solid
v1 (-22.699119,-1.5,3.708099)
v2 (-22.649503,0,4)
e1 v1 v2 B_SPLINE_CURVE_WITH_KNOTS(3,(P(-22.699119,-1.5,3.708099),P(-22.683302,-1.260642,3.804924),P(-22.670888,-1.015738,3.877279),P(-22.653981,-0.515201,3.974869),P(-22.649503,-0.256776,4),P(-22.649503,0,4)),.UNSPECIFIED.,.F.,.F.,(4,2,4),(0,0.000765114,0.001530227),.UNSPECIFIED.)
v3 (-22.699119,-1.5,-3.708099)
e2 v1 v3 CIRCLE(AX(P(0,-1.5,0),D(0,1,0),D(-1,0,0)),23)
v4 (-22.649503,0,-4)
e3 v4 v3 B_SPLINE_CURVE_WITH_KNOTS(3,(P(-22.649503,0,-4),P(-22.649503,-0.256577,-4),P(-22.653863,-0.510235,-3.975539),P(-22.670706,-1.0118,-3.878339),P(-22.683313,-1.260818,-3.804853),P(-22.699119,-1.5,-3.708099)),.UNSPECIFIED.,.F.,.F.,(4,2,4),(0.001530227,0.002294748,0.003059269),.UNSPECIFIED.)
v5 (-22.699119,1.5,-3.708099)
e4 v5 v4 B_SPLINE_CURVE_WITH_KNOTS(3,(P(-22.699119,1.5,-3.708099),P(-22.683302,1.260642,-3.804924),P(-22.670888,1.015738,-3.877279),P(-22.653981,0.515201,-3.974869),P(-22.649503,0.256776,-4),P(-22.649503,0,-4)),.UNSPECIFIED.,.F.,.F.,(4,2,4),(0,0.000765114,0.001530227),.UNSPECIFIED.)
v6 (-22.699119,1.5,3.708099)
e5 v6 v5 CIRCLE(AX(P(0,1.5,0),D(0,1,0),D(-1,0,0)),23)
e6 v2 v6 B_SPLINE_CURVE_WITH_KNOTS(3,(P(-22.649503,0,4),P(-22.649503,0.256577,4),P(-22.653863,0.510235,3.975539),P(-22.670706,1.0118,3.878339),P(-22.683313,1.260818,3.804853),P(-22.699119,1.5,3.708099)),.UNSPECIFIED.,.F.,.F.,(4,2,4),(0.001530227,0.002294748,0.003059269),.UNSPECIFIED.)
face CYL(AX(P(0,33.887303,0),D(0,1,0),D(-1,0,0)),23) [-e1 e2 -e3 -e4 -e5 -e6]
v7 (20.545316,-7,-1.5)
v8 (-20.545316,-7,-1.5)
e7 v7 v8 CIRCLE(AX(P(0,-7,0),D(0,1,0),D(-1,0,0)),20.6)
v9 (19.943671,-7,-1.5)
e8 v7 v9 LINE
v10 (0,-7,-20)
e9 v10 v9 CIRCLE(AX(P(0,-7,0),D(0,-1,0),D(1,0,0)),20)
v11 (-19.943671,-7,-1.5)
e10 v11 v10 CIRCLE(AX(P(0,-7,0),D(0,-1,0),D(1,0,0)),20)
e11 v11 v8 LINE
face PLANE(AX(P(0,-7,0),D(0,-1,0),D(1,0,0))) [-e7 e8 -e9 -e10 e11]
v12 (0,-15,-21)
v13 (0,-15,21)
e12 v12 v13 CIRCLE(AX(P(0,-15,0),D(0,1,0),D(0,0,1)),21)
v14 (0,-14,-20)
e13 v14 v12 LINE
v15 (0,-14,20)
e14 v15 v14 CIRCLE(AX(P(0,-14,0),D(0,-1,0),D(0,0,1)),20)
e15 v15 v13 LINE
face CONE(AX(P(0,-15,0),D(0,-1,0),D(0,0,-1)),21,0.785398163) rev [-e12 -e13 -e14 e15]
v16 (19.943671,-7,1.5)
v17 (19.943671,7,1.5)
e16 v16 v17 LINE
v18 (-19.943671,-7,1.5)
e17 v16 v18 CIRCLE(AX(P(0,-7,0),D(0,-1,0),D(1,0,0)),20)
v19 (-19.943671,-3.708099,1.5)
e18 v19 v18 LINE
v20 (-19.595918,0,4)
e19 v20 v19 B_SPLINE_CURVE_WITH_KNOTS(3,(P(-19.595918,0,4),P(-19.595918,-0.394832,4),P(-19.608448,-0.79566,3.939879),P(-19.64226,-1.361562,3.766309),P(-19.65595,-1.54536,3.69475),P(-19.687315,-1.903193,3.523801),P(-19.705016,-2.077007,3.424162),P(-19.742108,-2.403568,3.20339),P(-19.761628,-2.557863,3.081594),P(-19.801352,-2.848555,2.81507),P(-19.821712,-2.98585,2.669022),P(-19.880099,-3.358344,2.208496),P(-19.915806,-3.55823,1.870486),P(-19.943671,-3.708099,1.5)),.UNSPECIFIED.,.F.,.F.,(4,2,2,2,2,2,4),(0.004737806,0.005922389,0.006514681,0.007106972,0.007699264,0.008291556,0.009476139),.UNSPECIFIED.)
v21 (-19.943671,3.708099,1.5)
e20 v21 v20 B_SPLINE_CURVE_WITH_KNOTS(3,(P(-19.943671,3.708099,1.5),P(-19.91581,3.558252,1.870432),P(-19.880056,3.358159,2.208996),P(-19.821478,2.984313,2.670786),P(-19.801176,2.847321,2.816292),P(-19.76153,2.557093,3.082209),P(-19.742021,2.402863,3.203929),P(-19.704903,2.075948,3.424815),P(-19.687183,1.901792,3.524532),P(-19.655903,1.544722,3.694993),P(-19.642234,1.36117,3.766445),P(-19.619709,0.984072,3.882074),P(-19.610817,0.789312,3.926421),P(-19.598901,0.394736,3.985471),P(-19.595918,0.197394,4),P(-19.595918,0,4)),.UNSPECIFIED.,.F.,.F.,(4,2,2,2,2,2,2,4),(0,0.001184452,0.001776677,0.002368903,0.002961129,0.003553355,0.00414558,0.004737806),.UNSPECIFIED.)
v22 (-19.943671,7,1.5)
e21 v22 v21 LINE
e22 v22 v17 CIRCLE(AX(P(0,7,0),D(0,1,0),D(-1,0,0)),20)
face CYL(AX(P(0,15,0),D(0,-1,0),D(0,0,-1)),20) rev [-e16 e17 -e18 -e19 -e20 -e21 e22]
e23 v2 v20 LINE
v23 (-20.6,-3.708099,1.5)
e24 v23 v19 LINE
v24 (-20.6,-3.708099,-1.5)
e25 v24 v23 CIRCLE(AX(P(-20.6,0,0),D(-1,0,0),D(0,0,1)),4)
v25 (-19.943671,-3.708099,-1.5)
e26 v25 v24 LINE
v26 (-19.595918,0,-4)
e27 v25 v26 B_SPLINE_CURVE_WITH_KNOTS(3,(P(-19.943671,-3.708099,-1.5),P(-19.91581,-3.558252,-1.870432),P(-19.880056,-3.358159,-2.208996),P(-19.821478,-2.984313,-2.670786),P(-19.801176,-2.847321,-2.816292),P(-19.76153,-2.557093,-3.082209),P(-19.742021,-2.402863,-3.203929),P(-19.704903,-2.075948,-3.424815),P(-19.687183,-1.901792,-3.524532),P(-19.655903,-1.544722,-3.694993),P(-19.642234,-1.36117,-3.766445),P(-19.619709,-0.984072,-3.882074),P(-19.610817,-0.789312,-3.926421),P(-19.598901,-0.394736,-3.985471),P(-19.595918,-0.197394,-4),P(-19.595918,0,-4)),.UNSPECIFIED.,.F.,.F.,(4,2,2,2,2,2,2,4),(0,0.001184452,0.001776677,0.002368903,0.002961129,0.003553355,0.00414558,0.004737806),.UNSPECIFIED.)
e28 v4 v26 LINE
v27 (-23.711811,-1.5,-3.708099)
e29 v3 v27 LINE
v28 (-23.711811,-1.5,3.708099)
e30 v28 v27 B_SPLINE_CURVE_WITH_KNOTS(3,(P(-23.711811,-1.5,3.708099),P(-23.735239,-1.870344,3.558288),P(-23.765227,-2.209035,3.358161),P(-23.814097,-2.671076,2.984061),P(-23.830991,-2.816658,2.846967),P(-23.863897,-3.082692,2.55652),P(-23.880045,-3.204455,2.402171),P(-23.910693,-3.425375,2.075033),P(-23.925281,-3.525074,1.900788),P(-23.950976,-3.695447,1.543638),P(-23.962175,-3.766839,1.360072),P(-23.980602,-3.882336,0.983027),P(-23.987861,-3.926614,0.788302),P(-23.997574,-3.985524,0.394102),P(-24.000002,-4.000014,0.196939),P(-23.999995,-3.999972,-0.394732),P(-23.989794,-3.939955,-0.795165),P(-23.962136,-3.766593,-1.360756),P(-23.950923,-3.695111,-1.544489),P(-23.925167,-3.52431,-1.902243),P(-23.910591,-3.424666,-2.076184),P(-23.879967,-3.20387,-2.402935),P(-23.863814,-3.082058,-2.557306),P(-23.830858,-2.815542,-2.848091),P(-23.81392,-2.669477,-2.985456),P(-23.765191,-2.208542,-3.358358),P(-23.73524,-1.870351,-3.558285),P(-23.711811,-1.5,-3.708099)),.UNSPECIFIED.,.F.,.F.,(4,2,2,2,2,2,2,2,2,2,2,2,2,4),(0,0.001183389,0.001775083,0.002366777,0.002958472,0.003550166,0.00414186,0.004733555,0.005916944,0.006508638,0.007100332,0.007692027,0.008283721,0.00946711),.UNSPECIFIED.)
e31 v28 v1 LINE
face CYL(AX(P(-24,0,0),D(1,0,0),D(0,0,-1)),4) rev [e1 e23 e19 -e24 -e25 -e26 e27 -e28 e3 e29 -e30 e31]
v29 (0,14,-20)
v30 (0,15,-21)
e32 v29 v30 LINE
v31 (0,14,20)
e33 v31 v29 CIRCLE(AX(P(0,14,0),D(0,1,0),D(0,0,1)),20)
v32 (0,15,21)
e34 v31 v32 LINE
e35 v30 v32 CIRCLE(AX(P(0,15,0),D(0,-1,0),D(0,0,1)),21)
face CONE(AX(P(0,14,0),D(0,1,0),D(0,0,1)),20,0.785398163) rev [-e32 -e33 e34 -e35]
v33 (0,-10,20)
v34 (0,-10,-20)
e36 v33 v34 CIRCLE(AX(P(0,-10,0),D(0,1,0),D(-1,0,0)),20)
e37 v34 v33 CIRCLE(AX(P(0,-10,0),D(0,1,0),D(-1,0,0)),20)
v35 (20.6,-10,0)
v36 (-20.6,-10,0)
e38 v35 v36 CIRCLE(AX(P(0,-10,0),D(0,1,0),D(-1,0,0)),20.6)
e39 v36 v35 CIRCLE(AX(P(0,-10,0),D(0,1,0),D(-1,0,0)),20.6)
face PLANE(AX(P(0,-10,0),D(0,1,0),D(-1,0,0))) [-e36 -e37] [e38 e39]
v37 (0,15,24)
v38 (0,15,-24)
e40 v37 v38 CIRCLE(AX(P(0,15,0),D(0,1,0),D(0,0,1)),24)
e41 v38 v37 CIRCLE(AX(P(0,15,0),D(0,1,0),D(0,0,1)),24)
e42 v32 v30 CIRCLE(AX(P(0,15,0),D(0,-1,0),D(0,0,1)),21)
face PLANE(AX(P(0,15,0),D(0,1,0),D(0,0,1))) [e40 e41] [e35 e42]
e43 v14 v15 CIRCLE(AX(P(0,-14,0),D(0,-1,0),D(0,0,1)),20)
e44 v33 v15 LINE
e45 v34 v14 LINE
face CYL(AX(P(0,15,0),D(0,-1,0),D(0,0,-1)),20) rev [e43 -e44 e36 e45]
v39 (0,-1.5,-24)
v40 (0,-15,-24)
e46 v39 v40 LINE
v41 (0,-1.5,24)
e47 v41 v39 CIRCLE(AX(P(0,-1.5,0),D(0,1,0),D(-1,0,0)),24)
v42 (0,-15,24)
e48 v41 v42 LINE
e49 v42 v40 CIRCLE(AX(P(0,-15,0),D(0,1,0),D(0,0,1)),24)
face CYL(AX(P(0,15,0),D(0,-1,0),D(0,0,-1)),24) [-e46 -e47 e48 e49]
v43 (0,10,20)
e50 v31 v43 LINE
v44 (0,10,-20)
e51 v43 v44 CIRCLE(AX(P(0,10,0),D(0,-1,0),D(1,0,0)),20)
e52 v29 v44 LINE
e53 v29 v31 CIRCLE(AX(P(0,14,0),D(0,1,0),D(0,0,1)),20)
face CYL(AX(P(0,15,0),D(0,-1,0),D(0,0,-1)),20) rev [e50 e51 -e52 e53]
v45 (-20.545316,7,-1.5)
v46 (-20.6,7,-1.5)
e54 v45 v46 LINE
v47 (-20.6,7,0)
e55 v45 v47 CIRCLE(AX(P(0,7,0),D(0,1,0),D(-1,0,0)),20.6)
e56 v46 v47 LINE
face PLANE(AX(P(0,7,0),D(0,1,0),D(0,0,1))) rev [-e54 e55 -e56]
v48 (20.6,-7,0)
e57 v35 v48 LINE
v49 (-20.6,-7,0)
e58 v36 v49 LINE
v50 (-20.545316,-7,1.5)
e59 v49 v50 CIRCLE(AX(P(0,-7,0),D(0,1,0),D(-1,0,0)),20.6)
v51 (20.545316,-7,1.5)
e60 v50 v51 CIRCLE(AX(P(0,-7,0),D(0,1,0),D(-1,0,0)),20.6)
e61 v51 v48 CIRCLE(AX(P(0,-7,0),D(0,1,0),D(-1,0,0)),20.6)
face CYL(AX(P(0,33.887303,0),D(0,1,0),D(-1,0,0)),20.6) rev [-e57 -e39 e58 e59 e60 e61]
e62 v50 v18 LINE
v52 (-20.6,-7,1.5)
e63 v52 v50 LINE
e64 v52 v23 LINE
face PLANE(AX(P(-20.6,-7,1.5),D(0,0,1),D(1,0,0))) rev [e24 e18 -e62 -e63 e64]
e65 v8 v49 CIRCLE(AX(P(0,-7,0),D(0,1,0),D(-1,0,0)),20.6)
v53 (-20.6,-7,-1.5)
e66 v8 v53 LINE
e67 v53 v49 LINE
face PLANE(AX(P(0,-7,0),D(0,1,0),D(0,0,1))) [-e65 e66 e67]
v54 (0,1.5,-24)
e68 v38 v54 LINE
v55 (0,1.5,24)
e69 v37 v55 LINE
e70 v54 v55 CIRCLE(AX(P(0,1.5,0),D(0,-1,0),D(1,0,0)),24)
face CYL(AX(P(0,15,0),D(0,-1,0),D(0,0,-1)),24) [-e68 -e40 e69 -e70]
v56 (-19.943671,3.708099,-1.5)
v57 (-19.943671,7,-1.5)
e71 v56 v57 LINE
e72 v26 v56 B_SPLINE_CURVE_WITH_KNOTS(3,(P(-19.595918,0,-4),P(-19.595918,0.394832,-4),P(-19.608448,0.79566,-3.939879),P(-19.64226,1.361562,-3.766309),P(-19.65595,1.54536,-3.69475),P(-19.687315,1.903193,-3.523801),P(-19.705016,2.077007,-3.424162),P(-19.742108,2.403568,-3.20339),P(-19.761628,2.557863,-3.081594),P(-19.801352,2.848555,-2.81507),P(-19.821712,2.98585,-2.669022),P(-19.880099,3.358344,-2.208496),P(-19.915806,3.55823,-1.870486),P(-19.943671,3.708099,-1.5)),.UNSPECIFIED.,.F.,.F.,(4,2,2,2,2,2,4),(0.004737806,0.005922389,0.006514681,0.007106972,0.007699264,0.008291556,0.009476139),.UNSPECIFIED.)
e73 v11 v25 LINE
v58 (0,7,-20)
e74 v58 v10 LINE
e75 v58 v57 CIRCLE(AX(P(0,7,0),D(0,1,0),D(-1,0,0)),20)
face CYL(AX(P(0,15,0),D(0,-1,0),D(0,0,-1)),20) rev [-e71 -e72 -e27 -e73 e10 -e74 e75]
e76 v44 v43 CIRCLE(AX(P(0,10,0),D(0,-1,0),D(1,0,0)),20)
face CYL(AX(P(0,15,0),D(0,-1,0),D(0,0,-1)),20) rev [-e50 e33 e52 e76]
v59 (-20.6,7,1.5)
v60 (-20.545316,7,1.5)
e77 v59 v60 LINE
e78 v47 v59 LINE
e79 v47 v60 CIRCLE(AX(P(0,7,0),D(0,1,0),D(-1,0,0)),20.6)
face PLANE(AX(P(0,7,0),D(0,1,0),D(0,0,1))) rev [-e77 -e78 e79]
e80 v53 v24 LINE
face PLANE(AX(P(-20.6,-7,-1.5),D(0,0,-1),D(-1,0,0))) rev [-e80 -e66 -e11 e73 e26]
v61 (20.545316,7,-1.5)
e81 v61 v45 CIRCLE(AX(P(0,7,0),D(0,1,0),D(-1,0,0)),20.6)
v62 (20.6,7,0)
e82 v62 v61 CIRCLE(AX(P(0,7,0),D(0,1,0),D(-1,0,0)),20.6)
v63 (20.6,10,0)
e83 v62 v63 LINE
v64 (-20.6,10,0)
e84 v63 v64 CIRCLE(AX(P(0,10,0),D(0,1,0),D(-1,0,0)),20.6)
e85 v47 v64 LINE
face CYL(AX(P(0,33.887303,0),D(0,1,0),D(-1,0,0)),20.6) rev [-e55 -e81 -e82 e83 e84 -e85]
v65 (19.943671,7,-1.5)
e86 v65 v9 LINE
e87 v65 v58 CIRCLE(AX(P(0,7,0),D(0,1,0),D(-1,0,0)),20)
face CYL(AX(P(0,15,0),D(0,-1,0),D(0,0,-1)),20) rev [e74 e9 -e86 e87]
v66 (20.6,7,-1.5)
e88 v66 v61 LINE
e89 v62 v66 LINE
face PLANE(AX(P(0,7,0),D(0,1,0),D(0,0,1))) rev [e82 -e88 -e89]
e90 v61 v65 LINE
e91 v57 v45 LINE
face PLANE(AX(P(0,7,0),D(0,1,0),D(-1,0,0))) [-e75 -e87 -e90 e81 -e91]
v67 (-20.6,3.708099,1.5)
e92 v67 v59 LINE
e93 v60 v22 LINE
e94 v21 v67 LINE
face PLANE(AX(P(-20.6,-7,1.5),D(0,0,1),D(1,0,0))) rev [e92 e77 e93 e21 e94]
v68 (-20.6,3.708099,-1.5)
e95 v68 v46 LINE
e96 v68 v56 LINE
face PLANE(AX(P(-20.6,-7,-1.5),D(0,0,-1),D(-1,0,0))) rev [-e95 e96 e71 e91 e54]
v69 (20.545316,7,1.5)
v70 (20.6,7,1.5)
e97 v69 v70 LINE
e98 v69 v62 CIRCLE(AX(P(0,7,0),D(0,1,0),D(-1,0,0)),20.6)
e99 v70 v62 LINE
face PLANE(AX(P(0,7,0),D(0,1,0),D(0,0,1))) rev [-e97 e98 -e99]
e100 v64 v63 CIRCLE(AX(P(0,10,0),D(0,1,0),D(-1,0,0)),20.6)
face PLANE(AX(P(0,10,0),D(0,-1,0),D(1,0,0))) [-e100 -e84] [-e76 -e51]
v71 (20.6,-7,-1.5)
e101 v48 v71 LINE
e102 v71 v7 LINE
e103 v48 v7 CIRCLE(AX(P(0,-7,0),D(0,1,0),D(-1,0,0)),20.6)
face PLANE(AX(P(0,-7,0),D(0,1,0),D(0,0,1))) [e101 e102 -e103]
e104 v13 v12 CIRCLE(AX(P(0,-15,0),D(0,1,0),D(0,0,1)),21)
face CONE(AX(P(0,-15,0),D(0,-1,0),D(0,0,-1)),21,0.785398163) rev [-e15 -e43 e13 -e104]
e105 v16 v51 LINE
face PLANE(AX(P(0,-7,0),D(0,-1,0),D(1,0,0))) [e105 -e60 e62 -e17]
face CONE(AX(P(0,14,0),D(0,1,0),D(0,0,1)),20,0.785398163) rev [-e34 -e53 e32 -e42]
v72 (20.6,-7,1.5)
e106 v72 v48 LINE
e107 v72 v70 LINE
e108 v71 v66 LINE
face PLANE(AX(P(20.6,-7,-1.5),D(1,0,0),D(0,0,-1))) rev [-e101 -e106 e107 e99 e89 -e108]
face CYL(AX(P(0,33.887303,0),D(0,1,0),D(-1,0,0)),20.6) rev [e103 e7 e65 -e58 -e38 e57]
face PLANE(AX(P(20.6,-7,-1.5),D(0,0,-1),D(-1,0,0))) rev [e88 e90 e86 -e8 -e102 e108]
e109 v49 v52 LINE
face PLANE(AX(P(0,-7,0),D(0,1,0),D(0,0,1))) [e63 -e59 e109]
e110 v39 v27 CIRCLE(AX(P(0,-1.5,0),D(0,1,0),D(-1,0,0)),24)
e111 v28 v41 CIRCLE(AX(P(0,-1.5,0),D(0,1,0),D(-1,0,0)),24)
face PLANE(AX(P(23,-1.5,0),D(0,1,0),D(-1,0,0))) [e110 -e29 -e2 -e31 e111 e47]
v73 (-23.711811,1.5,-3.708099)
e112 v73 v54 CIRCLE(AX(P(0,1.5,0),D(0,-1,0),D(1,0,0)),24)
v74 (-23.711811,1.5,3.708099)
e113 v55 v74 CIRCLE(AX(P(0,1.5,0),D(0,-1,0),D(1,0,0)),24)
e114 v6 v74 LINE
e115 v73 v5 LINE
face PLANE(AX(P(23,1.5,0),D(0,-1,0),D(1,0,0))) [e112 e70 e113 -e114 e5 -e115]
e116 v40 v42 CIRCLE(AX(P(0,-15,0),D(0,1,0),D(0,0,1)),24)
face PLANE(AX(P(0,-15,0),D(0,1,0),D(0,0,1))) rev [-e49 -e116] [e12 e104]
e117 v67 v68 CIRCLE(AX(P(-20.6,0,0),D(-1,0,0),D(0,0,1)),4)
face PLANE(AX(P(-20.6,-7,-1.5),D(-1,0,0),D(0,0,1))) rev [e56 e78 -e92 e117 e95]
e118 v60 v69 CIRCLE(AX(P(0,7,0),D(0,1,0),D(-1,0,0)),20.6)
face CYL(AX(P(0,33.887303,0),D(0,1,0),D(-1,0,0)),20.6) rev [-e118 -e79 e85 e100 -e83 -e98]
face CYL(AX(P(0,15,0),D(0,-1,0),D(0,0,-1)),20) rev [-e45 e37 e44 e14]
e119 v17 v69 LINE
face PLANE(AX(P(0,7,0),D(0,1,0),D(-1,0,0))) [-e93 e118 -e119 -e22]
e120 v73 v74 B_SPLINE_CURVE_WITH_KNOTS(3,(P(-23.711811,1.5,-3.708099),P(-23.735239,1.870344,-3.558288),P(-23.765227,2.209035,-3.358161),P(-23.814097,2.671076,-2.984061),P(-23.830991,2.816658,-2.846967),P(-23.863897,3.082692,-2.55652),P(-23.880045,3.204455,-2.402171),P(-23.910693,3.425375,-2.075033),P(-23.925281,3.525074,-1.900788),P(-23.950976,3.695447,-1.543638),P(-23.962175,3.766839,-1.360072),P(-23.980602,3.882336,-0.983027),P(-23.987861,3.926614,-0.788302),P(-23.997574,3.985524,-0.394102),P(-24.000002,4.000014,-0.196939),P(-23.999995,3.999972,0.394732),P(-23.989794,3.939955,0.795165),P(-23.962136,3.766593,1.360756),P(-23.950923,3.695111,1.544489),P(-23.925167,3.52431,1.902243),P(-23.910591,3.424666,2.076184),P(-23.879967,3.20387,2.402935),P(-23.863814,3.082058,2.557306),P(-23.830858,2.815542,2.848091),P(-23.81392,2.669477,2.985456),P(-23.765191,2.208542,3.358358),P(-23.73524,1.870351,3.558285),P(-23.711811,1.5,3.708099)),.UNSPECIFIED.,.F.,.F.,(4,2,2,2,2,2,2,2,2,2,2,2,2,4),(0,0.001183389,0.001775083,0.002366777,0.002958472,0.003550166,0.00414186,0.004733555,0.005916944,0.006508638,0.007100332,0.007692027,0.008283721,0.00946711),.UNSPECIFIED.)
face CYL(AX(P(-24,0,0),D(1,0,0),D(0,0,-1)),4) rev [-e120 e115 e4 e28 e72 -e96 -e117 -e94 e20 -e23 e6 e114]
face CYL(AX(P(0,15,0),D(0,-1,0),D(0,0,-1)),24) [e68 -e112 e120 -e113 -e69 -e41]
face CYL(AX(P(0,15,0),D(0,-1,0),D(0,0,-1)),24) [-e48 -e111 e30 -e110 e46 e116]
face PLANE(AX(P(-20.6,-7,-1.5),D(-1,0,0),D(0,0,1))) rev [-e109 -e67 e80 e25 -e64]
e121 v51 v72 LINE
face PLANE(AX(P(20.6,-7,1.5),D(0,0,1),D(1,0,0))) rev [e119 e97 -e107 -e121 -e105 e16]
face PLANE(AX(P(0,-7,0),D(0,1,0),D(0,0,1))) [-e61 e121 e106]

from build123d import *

# Parameters (mm, degrees)
SKETCH_1_R          = 24
SKETCH_1_R_2        = 20
EXTRUDE_1_DEPTH     = 15
SKETCH_2_W          = 20.6
SKETCH_2_H          = 3
SKETCH_2_W_2        = 4.5
SKETCH_5_W          = 3.1
SKETCH_5_H          = 3
CUT_EXTRUDE_1_DEPTH = 7
SKETCH_6_R          = 4
CUT_EXTRUDE_2_DEPTH = 38.107950631
CHAMFER_1_SIZE      = 1


with BuildPart() as part:
    # 草图1 → 凸台-拉伸1 (new, symmetric)
    with BuildSketch(Plane(origin=(0, 0, 0), x_dir=(1, 0, 0), z_dir=(0, 1, 0))):
        with Locations(Location((0, 0, 0), (0, 0, 270))):
            Circle(SKETCH_1_R)
        with Locations(Location((0, 0, 0), (0, 0, 270))):
            Circle(SKETCH_1_R_2, mode=Mode.SUBTRACT)
    extrude(amount=EXTRUDE_1_DEPTH, both=True)

    # 草图2 → 切除-旋转1 (revolve, cut)
    with BuildSketch(Plane.XY, mode=Mode.PRIVATE) as cut_revolve_1_sk:
        with Locations((10.3, 8.5)):
            Rectangle(SKETCH_2_W, SKETCH_2_H)
        with Locations((10.3, -8.5)):
            Rectangle(SKETCH_2_W, SKETCH_2_H)
        with Locations((25.25, 0)):
            Rectangle(SKETCH_2_W_2, SKETCH_2_H)
    revolve(cut_revolve_1_sk.sketch.rotate(Axis((0, 33.887302741, 0), (0, -1, 0)), 180), axis=Axis((0, 33.887302741, 0), (0, -1, 0)), mode=Mode.SUBTRACT)

    # 草图5 → 切除-拉伸1 (cut, symmetric)
    with BuildSketch(Plane(origin=(0, 0, 0), x_dir=(1, 0, 0), z_dir=(0, 1, 0))):
        with Locations((19.05, 0)):
            Rectangle(SKETCH_5_W, SKETCH_5_H)
        with Locations((-19.05, 0)):
            Rectangle(SKETCH_5_W, SKETCH_5_H)
    extrude(amount=CUT_EXTRUDE_1_DEPTH, both=True, mode=Mode.SUBTRACT)

    # 草图6 → 切除-拉伸2 (cut, through all)
    with BuildSketch(Plane(origin=(0, 0, 0), x_dir=(0, 0, -1), z_dir=(1, 0, 0))):
        with Locations(Location((0, 0, 0), (0, 0, 22.024312837))):
            Circle(SKETCH_6_R)
    extrude(amount=-CUT_EXTRUDE_2_DEPTH, mode=Mode.SUBTRACT)

    # 倒角1
    chamfer_1_edges = [part.edges().sort_by_distance(p)[0] for p in [
        (0, -15, -20),
        (0, 15, -20),
    ]]
    chamfer(chamfer_1_edges, length=CHAMFER_1_SIZE)


solid = part.part
